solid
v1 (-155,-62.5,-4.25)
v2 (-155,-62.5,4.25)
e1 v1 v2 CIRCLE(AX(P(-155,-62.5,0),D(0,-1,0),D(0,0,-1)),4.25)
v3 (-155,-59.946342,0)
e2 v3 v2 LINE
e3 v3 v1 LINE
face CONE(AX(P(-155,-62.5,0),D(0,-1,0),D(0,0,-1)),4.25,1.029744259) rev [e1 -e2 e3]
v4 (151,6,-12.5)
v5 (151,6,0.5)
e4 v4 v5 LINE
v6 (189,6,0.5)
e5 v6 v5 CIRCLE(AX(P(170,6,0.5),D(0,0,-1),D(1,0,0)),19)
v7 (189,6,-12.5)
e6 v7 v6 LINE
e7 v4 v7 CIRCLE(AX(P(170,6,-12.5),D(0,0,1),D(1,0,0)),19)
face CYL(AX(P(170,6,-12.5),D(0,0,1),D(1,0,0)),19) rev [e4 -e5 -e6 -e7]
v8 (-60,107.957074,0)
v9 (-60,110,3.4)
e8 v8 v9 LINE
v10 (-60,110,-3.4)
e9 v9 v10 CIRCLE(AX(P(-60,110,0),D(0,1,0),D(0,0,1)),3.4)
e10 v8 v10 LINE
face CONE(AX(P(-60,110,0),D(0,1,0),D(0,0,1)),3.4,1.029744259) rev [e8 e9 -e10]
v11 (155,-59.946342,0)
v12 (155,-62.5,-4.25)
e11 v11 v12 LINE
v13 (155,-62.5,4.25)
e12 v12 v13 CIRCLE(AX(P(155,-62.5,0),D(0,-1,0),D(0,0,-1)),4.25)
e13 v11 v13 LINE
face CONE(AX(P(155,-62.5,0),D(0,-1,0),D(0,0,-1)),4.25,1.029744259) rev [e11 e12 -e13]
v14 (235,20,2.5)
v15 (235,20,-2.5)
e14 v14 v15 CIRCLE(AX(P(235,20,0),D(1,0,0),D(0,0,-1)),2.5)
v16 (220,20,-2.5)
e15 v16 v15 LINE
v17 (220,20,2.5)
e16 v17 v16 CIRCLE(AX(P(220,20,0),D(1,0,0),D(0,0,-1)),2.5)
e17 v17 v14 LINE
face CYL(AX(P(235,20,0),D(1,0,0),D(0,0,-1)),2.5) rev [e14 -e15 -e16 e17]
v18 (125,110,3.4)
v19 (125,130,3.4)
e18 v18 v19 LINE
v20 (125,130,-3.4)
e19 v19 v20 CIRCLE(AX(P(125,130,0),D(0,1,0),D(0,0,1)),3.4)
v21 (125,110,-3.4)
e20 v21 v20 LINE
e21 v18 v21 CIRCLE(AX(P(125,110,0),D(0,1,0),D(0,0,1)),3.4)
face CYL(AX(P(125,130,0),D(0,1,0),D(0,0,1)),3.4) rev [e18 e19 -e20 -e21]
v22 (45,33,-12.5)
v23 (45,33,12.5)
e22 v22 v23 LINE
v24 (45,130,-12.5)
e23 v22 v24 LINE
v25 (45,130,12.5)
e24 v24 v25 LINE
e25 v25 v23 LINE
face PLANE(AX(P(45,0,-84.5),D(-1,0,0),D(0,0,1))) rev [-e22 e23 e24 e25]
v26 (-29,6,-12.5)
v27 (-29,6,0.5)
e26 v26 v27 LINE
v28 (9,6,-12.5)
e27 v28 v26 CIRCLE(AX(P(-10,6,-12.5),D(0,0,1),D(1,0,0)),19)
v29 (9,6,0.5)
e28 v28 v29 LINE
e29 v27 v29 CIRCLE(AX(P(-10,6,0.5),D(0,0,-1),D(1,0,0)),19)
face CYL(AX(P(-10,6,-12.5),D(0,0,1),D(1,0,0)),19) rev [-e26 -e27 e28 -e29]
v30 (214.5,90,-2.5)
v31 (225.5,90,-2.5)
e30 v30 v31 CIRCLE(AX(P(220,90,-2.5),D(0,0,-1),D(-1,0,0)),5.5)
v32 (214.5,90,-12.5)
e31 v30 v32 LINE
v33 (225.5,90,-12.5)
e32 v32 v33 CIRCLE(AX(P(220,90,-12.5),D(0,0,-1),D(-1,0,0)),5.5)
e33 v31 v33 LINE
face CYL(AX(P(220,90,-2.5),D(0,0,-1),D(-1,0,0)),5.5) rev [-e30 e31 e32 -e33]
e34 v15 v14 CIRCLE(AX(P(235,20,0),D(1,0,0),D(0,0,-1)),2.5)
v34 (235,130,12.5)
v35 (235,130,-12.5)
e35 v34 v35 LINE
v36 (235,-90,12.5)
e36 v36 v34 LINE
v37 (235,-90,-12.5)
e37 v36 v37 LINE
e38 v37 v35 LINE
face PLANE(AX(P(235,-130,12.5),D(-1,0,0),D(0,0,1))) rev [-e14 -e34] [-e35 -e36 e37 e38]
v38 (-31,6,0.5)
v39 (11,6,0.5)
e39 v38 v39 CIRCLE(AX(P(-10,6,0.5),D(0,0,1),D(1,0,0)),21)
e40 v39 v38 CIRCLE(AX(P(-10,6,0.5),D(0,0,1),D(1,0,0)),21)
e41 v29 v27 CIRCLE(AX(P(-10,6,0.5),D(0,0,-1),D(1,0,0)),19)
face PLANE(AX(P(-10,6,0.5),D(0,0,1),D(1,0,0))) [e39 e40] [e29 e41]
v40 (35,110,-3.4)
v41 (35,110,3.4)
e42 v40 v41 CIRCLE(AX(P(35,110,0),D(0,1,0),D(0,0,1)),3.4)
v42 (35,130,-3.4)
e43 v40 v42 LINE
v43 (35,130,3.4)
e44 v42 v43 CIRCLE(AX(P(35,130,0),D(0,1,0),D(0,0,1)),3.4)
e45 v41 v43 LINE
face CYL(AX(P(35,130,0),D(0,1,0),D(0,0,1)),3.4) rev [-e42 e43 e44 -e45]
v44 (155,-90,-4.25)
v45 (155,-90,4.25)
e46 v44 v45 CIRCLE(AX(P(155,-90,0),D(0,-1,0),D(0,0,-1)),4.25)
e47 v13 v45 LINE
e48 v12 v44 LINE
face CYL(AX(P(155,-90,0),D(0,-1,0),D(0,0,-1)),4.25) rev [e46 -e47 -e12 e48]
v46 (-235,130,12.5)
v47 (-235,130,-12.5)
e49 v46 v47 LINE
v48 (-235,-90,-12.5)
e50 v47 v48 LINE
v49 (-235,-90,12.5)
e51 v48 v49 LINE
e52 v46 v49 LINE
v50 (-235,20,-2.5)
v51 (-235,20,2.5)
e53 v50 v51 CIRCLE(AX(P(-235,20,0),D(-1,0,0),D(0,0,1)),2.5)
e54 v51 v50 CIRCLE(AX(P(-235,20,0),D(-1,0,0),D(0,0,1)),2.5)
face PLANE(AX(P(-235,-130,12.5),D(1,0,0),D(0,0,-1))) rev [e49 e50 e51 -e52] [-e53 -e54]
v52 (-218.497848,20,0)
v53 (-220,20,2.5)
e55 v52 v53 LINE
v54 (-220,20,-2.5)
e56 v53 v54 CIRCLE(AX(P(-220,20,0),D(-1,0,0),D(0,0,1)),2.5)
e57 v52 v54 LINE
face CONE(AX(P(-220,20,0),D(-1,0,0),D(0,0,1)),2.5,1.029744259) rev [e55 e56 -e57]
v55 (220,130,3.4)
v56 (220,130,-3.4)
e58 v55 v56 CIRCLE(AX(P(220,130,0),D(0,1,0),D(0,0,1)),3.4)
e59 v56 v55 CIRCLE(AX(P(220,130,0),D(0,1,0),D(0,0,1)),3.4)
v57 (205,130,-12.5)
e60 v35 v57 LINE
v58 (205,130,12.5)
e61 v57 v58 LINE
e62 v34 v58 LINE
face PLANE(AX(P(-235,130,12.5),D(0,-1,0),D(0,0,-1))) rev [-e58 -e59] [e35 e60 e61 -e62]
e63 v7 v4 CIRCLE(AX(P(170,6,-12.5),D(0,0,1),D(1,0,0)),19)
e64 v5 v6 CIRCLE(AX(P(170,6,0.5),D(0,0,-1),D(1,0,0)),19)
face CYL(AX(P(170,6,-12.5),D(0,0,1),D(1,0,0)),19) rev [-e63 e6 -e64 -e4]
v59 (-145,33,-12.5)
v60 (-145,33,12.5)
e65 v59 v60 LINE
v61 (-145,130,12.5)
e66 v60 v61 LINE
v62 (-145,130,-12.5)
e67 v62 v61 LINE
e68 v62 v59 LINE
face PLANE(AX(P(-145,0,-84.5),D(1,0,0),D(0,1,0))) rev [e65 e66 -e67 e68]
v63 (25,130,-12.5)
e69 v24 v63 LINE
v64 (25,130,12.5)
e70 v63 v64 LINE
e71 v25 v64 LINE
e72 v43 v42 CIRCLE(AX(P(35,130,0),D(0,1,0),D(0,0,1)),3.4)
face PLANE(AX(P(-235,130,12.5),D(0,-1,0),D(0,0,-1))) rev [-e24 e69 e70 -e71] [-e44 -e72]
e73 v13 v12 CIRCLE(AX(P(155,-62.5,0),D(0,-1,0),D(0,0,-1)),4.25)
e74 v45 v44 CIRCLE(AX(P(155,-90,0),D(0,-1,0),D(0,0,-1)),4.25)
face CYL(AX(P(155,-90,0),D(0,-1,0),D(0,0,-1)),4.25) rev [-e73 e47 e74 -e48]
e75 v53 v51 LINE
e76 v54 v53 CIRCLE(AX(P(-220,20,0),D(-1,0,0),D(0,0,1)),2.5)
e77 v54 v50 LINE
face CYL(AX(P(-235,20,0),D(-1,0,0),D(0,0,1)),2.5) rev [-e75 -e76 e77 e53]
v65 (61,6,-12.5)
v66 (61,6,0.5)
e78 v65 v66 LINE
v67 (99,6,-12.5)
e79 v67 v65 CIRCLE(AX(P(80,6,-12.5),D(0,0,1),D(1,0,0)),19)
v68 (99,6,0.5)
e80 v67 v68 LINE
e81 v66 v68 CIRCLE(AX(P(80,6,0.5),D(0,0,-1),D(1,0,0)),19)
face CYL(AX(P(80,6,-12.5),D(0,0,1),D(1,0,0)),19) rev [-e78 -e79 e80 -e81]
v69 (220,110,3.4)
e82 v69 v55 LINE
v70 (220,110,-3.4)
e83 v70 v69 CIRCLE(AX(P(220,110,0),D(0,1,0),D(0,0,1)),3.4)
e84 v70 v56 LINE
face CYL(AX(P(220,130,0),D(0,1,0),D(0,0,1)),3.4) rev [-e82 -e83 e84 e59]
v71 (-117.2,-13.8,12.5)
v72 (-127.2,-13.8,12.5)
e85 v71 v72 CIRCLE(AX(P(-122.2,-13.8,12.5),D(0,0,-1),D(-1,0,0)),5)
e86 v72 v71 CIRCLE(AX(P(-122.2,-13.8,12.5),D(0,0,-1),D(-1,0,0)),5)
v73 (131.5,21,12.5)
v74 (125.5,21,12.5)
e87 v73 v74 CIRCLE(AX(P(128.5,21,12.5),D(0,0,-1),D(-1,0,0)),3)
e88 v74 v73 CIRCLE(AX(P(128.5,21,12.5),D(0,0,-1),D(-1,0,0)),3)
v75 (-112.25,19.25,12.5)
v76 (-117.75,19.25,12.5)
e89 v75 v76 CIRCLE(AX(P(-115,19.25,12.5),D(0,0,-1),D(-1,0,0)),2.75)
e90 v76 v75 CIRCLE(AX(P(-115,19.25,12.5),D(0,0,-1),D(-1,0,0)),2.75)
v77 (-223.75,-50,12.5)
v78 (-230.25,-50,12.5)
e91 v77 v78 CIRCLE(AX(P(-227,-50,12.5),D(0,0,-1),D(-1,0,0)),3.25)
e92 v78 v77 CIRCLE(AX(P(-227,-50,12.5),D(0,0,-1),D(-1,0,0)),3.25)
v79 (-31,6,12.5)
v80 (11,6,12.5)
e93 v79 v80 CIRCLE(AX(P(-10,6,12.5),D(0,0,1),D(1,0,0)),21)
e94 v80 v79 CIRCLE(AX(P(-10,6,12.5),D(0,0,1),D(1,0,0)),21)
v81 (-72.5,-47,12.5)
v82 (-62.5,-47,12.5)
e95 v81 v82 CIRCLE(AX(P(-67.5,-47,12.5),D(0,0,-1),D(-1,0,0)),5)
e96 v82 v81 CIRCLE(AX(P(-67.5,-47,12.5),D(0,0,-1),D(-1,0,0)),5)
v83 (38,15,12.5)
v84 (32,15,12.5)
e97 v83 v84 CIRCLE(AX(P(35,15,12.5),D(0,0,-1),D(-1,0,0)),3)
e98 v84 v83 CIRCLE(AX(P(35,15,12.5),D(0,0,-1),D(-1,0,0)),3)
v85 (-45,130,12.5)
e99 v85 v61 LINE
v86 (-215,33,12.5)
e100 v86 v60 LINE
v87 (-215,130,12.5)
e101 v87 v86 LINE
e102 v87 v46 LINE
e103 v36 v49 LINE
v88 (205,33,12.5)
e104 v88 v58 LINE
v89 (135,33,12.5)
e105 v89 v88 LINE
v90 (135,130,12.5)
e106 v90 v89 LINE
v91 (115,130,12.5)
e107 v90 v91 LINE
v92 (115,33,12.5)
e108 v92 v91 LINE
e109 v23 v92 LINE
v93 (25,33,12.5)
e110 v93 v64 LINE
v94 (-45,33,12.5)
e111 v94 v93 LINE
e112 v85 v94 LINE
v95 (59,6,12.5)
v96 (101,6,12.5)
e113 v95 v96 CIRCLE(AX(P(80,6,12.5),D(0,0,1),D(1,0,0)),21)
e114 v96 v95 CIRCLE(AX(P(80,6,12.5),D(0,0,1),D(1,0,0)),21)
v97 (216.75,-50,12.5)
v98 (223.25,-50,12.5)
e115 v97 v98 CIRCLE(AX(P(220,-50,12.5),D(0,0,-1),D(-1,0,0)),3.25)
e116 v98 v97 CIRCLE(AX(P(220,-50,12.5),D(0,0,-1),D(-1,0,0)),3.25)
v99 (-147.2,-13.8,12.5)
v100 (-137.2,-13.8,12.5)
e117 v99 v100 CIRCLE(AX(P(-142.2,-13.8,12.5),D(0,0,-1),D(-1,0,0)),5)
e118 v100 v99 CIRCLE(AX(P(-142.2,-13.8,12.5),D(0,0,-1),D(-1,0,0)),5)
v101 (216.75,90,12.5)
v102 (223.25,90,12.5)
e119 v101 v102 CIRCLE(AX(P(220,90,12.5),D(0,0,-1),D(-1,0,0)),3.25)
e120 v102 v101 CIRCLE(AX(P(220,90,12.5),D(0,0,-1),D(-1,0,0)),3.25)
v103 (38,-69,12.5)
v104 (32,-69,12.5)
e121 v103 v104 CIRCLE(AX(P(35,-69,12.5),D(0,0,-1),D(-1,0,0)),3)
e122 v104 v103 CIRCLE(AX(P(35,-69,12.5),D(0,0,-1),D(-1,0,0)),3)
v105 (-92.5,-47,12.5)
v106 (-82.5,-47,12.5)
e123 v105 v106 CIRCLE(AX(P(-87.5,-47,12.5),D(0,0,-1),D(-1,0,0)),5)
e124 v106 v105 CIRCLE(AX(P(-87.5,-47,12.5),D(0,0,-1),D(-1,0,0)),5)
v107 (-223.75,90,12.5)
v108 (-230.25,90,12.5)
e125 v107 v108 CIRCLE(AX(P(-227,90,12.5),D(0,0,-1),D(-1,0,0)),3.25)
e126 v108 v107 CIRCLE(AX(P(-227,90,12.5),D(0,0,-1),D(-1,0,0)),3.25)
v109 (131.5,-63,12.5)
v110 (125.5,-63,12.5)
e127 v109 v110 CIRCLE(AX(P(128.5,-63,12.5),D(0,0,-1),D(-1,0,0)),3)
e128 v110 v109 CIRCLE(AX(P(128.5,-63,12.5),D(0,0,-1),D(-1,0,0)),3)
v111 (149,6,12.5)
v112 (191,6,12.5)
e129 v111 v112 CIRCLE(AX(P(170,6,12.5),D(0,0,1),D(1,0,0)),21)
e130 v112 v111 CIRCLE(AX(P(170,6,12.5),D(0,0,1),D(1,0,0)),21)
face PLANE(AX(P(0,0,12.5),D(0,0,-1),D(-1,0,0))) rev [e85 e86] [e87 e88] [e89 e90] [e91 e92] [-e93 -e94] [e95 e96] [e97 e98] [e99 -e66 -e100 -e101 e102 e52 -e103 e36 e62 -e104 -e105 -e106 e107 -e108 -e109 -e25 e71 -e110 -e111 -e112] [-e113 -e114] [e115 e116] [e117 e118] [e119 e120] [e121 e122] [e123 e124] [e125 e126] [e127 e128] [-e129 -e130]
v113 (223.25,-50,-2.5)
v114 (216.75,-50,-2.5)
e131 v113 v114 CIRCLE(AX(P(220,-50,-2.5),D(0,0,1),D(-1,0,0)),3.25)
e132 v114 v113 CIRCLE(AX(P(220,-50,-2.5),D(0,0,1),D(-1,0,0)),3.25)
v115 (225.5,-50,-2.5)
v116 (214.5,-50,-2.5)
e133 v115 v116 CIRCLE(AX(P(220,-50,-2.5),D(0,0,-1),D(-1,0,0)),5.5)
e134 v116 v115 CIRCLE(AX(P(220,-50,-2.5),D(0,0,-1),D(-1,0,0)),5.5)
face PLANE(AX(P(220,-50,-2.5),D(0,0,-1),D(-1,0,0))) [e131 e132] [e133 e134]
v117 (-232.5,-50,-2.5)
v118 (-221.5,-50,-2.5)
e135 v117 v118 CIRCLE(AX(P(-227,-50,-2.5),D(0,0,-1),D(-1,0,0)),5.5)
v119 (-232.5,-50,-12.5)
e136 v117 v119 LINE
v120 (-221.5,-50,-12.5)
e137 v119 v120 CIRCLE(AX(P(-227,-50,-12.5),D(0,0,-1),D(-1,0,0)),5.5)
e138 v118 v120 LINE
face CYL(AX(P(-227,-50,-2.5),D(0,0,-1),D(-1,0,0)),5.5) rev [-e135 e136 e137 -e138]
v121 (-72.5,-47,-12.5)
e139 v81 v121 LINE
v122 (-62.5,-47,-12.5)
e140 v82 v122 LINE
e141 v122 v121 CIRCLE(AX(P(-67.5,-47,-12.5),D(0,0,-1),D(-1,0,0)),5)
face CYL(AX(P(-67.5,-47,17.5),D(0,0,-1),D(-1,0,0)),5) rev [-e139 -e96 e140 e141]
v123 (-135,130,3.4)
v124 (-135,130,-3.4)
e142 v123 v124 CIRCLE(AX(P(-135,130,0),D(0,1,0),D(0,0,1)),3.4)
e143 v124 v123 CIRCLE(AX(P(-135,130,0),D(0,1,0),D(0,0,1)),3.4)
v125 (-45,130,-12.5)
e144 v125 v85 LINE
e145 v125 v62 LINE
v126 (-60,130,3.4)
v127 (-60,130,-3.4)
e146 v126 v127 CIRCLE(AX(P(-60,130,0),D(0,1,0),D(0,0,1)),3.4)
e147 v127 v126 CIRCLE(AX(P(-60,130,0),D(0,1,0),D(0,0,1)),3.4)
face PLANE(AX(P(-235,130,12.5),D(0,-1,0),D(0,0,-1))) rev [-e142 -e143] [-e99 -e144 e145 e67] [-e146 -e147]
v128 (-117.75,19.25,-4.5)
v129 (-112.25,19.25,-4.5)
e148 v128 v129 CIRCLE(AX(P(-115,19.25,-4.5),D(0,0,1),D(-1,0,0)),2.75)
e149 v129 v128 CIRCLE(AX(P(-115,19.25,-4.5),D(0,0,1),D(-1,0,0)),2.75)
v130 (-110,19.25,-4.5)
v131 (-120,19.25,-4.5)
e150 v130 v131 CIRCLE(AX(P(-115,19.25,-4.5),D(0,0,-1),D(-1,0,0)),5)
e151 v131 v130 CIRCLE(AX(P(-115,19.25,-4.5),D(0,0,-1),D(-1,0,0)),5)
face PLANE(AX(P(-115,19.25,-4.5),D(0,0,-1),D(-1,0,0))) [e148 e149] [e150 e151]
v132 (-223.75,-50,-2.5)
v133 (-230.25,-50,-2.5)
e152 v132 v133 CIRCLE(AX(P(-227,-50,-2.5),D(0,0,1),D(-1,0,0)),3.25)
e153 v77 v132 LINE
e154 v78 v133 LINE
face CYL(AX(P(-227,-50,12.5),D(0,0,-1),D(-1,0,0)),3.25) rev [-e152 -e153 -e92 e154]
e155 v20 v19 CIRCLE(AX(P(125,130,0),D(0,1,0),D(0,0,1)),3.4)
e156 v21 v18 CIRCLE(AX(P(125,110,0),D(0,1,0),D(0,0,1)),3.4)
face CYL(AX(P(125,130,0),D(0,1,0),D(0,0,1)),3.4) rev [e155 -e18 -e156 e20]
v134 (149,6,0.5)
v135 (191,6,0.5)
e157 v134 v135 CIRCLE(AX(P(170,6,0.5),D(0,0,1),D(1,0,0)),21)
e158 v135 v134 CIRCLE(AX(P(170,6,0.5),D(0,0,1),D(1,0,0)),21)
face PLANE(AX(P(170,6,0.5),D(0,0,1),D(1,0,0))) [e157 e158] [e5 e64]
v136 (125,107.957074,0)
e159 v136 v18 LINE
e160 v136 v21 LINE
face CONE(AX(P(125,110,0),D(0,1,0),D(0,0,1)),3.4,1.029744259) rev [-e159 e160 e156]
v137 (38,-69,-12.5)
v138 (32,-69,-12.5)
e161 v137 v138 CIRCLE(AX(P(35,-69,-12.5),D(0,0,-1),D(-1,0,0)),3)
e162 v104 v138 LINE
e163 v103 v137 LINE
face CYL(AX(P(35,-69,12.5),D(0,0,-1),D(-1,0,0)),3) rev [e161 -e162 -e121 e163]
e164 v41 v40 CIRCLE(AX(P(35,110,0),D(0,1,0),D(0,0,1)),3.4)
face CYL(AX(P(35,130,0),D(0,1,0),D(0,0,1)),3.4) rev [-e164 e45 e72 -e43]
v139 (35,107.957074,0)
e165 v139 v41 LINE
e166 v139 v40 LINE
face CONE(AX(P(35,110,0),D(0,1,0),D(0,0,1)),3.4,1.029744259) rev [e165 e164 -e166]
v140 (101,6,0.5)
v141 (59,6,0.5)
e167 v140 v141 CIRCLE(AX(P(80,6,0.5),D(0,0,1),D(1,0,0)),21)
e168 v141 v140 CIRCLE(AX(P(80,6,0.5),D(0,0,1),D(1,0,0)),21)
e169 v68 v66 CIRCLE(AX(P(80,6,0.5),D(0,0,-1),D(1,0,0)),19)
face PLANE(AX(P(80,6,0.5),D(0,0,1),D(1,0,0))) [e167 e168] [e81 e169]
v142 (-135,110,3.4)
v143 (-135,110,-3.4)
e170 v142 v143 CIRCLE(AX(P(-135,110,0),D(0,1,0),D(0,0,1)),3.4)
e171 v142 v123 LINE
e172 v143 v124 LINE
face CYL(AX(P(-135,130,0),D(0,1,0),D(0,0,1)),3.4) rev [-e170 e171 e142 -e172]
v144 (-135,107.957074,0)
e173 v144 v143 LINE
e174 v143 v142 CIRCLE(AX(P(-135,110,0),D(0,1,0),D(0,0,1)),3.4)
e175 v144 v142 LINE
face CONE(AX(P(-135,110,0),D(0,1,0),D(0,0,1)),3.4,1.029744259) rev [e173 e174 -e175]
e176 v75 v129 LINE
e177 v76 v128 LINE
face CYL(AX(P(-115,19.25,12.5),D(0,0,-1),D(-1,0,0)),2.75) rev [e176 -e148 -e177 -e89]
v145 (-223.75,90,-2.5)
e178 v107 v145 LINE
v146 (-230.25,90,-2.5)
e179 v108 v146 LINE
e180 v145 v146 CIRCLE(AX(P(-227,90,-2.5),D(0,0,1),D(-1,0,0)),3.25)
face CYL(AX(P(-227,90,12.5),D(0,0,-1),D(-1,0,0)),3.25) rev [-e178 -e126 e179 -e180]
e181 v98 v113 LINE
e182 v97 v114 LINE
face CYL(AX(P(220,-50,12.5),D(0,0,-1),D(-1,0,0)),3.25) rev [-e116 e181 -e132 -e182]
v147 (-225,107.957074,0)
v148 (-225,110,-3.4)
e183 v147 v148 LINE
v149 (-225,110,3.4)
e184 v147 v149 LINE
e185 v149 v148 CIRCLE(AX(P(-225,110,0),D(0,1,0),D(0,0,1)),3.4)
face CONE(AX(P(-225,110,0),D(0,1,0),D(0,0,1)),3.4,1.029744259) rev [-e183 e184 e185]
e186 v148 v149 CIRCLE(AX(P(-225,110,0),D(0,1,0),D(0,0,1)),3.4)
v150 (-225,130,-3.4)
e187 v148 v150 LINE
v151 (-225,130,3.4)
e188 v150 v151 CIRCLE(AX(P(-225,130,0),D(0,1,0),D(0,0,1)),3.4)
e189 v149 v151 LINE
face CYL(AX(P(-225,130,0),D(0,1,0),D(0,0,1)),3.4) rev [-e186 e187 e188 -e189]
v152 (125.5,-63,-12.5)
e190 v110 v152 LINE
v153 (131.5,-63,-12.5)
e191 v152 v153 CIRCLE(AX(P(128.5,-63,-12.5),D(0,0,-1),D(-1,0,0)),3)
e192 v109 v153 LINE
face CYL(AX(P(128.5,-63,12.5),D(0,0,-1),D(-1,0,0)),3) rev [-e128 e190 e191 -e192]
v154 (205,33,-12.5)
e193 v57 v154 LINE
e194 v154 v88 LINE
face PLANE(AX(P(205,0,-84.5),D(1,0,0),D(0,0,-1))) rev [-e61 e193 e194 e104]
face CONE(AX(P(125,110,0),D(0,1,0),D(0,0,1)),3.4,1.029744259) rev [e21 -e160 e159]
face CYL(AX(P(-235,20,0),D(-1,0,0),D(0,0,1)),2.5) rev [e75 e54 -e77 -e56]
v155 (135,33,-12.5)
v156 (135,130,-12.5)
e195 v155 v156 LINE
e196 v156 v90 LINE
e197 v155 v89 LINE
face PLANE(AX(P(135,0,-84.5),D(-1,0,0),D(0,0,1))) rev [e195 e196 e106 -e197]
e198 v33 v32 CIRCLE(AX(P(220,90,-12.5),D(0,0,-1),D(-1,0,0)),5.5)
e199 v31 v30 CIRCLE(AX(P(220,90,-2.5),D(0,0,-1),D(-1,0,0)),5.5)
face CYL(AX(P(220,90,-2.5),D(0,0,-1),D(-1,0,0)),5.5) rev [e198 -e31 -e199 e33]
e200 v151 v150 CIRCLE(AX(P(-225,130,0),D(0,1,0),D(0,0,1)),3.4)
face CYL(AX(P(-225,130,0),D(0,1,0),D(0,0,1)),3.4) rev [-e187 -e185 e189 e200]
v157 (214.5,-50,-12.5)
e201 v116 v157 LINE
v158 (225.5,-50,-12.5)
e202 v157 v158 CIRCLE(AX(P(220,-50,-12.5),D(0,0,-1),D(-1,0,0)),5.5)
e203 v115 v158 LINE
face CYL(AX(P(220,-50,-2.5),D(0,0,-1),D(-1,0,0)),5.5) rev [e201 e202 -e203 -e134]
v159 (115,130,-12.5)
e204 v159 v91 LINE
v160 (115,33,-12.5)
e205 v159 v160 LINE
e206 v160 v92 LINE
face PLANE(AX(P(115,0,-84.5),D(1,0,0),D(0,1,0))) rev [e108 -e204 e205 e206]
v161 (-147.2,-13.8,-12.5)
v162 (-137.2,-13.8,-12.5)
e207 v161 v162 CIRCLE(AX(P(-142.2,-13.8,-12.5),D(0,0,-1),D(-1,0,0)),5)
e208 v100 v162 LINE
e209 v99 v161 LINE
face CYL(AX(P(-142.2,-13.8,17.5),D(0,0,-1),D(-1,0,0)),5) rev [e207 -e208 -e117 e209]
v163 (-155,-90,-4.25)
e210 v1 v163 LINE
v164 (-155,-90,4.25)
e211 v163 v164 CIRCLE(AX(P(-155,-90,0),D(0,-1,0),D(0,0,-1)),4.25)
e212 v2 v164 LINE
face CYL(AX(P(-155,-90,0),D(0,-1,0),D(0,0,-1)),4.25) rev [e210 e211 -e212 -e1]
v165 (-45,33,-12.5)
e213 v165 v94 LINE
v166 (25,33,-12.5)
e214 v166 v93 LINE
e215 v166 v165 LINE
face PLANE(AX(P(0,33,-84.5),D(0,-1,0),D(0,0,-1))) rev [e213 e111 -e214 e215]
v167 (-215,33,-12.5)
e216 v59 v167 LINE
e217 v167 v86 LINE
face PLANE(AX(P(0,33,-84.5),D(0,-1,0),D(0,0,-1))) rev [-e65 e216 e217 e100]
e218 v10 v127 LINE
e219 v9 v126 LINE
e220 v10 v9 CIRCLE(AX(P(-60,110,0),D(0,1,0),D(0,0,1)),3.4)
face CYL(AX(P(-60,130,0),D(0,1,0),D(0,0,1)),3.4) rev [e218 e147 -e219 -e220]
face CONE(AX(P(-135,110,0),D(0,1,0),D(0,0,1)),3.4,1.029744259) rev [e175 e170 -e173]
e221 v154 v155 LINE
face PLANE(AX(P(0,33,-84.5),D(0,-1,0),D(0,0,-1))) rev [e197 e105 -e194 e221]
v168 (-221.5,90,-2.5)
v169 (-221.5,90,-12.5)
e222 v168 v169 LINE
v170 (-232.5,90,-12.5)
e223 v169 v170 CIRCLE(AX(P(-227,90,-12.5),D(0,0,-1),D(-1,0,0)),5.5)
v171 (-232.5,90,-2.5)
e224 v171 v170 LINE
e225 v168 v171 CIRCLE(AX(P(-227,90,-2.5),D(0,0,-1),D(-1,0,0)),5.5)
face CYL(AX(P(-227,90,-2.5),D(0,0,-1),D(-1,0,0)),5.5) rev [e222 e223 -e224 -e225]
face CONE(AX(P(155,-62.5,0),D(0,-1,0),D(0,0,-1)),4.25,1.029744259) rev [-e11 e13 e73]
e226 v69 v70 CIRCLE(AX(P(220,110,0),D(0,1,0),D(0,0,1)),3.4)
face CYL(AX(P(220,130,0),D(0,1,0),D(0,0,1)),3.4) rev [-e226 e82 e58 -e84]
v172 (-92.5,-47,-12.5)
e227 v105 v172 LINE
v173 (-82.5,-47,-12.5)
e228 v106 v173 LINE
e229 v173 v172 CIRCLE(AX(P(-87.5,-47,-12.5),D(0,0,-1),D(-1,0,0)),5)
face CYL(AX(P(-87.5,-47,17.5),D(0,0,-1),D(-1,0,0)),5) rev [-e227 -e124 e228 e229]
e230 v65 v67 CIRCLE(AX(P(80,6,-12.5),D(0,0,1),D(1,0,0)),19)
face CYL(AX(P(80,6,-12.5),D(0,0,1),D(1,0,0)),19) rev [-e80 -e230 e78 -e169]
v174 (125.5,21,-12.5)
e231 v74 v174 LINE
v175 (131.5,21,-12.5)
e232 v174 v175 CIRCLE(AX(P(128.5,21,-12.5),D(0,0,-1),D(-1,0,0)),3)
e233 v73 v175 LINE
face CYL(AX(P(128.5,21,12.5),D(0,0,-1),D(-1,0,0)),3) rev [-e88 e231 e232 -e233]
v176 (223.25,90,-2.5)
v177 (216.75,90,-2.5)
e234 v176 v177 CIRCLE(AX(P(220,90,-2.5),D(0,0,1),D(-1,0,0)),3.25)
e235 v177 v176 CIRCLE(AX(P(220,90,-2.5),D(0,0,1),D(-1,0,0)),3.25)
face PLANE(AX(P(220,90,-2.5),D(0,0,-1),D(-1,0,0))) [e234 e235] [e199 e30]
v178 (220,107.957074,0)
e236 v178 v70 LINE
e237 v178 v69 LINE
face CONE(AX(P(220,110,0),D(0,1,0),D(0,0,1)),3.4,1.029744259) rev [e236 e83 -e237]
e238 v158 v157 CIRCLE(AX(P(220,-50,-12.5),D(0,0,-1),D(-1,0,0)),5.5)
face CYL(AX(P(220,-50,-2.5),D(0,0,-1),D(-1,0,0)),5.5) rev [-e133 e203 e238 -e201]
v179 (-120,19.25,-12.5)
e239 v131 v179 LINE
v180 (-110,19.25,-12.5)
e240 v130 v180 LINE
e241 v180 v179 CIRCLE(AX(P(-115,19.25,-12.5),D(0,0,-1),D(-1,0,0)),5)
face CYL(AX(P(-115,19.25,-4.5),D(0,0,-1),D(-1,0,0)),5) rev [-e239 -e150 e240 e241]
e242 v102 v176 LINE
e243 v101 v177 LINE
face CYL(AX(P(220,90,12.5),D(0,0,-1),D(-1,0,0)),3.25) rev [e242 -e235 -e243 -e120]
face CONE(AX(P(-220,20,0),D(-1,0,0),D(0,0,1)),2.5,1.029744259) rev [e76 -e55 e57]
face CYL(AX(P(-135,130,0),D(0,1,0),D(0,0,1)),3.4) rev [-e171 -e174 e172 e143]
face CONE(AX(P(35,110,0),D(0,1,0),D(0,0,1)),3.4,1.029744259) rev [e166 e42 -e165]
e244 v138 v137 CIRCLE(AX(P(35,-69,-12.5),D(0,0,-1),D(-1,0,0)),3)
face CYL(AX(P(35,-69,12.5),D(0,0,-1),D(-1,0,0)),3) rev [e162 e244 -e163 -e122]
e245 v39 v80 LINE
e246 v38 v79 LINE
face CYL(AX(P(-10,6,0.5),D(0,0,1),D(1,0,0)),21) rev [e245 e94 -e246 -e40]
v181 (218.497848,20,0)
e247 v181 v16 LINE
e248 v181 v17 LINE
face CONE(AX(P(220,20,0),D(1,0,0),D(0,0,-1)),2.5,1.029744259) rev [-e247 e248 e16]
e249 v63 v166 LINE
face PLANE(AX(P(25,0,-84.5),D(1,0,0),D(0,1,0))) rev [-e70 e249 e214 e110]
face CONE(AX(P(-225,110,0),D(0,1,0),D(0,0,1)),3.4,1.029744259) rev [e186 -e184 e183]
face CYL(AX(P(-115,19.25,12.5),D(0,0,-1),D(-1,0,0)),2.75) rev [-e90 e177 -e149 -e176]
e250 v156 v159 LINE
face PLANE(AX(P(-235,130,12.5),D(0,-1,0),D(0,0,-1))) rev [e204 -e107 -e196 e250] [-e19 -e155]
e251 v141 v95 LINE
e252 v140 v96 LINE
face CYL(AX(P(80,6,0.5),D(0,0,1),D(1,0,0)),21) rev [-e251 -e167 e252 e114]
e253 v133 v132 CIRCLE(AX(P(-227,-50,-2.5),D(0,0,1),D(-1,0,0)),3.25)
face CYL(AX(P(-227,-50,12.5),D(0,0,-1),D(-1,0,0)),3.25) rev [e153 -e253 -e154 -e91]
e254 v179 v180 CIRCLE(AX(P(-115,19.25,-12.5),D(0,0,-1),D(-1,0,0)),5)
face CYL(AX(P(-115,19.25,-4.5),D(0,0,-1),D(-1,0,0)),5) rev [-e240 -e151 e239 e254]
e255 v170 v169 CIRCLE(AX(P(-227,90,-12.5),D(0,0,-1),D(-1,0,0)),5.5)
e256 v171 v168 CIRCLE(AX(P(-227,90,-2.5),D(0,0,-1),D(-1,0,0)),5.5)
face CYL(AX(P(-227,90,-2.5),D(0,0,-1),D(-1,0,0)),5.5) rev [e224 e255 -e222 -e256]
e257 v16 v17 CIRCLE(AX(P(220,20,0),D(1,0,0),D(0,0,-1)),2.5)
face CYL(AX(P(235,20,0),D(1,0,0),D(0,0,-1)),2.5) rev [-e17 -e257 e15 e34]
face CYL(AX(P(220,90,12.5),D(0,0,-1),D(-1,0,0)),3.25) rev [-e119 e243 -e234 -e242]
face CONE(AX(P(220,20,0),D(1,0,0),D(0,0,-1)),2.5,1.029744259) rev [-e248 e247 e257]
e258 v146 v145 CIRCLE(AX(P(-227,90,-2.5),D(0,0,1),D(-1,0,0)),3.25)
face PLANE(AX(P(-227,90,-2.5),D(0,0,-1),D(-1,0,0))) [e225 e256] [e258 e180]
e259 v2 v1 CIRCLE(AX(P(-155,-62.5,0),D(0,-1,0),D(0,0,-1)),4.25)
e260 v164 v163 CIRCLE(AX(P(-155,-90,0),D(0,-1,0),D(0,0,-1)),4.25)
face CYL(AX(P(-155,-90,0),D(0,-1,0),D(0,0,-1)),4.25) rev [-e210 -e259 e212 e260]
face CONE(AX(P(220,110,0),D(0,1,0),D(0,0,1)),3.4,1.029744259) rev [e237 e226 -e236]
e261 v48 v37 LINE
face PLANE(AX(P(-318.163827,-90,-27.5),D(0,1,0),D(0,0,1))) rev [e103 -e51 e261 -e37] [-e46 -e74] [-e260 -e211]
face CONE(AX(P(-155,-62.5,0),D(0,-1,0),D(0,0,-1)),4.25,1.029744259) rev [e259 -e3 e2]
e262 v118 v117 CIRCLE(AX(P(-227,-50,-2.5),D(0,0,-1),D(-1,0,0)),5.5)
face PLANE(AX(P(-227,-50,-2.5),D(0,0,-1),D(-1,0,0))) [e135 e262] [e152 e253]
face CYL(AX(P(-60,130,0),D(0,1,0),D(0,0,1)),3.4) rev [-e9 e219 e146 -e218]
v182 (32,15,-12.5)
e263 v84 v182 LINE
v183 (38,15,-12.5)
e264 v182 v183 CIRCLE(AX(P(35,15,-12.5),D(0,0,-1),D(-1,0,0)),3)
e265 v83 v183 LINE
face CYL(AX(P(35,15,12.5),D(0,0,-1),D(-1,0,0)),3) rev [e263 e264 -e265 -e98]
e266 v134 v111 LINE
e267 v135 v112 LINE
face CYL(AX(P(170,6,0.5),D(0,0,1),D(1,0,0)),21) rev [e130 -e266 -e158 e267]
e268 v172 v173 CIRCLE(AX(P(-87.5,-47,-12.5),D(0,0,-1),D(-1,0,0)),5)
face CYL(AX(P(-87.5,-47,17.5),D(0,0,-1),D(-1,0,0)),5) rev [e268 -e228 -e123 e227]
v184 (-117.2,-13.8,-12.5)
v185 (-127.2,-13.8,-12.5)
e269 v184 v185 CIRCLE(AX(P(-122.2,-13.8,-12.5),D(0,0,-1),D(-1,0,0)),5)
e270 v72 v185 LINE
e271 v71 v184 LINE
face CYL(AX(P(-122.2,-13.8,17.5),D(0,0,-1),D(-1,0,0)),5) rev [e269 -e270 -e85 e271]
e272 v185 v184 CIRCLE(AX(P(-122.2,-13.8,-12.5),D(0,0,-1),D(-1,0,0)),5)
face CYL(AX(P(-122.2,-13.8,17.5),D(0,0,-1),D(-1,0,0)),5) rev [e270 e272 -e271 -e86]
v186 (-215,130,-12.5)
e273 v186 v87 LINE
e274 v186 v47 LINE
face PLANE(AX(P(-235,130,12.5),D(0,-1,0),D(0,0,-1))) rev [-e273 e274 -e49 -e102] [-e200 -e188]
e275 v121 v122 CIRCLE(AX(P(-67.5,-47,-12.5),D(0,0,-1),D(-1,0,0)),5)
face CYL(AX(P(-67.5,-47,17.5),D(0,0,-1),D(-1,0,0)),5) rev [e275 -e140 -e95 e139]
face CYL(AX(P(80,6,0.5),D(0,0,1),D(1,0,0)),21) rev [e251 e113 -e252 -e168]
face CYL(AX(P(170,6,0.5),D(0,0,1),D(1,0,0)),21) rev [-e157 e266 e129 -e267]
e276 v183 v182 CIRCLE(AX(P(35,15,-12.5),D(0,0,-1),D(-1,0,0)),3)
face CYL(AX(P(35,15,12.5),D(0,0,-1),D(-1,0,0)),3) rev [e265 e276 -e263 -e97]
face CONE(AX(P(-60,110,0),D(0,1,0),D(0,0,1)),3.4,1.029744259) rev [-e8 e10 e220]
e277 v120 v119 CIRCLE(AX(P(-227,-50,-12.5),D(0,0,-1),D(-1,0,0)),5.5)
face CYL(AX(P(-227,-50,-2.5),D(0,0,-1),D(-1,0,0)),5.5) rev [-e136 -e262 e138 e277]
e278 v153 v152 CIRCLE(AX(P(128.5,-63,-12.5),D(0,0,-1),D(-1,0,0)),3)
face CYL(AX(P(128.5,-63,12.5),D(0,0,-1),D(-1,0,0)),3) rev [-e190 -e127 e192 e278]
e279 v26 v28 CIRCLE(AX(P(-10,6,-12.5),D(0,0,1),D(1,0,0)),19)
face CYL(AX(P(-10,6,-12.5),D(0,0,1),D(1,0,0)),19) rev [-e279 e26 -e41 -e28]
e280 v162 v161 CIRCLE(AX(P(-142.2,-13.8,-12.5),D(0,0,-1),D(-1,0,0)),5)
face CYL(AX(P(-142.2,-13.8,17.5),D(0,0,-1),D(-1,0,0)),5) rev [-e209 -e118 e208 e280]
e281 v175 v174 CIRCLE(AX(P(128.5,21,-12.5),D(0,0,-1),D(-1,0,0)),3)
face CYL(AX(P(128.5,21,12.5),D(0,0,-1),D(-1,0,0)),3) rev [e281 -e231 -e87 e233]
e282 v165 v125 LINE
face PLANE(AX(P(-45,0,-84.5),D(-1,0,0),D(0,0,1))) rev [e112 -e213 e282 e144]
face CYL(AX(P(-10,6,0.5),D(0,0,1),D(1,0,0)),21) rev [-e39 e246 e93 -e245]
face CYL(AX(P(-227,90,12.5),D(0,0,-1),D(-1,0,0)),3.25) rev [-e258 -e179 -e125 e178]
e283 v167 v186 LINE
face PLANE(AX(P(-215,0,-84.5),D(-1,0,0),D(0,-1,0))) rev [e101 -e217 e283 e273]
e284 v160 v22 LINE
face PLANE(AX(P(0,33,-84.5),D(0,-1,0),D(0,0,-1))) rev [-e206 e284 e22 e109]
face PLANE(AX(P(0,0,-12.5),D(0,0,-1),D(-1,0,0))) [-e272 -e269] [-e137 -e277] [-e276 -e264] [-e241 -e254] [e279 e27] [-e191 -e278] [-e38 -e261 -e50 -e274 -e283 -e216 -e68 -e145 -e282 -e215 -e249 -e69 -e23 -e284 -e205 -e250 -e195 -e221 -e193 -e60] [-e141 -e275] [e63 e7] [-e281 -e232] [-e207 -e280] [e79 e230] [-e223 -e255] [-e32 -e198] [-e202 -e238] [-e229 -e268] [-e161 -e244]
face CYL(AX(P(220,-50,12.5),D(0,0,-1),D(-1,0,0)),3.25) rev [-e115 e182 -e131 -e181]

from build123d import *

# Parameters (mm, degrees)
SKETCH1_W                       = 470
SKETCH1_H                       = 260
BOSS_EXTRUDE1_DEPTH             = 12.5
SKETCH4_W                       = 70
SKETCH4_H                       = 97
CUT_EXTRUDE3_DEPTH              = 97
SKETCH8_W                       = 627.570760349
SKETCH8_H                       = 104.374926458
CUT_EXTRUDE7_DEPTH              = 40
M8_TAPPED_HOLE1_D               = 6.8
M8_TAPPED_HOLE1_DEPTH           = 20
M8_TAPPED_HOLE1_TIP             = 2.042926105
M10_TAPPED_HOLE1_D              = 8.5
M10_TAPPED_HOLE1_DEPTH          = 27.5
M10_TAPPED_HOLE1_TIP            = 2.553657631
SKETCH17_R                      = 19
CUT_EXTRUDE10_DEPTH             = 270.722079185
SKETCH18_R                      = 21
CUT_EXTRUDE11_DEPTH             = 12
SKETCH22_R                      = 3
CUT_EXTRUDE13_DEPTH             = 270.722079185
SKETCH23_R                      = 3.25
CUT_EXTRUDE14_DEPTH             = 270.722079185
SKETCH24_R                      = 5.5
CUT_EXTRUDE15_DEPTH             = 10
LPATTERN1_COUNT                 = 2
LPATTERN1_PITCH                 = 447
SKETCH26_R                      = 2.75
CUT_EXTRUDE17_DEPTH             = 270.722079185
SKETCH27_R                      = 5
CUT_EXTRUDE18_DEPTH             = 8
SKETCH28_R                      = 5
CUT_EXTRUDE19_DEPTH             = 30
M6_TAPPED_HOLE1_D               = 5
M6_TAPPED_HOLE1_DEPTH           = 15
M6_TAPPED_HOLE1_TIP             = 1.502151548
M6_TAPPED_HOLE1_ON_FACE_2_D     = 5
M6_TAPPED_HOLE1_ON_FACE_2_DEPTH = 15
M6_TAPPED_HOLE1_ON_FACE_2_TIP   = 1.502151548


with BuildPart() as part:
    # Sketch1 → Boss-Extrude1 (new, symmetric)
    with BuildSketch(Plane.XY):
        Rectangle(SKETCH1_W, SKETCH1_H)
    extrude(amount=BOSS_EXTRUDE1_DEPTH, both=True)

    # Sketch4 → Cut-Extrude3 (cut)
    with BuildSketch(Plane.XY.offset(12.5)):
        with Locations((-180, 81.5)):
            Rectangle(SKETCH4_W, SKETCH4_H)
        with Locations((-10, 81.5)):
            Rectangle(SKETCH4_W, SKETCH4_H)
        with Locations((80, 81.5)):
            Rectangle(SKETCH4_W, SKETCH4_H)
        with Locations((170, 81.5)):
            Rectangle(SKETCH4_W, SKETCH4_H)
    extrude(amount=-CUT_EXTRUDE3_DEPTH, mode=Mode.SUBTRACT)

    # Sketch8 → Cut-Extrude7 (cut)
    with BuildSketch(Plane.XY.offset(12.5)):
        with Locations((-4.378447024, -142.187463229)):
            Rectangle(SKETCH8_W, SKETCH8_H)
    extrude(amount=-CUT_EXTRUDE7_DEPTH, mode=Mode.SUBTRACT)

    # M8 Tapped Hole1
    with Locations(Plane(origin=(0, 130, 0), x_dir=(1, 0, 0), z_dir=(0, 1, 0))):
        with Locations((-225, 0), (-135, 0), (35, 0), (125, 0), (220, 0), (-60, 0)):
            Hole(M8_TAPPED_HOLE1_D / 2, depth=M8_TAPPED_HOLE1_DEPTH)
            with Locations((0, 0, -(M8_TAPPED_HOLE1_DEPTH + M8_TAPPED_HOLE1_TIP / 2))):  # 118° drill point
                Cone(0, M8_TAPPED_HOLE1_D / 2, M8_TAPPED_HOLE1_TIP, mode=Mode.SUBTRACT)

    # M10 Tapped Hole1
    with Locations(Plane(origin=(0, -90, 0), x_dir=(-1, 0, 0), z_dir=(0, -1, 0))):
        with Locations((-155, 0), (155, 0)):
            Hole(M10_TAPPED_HOLE1_D / 2, depth=M10_TAPPED_HOLE1_DEPTH)
            with Locations((0, 0, -(M10_TAPPED_HOLE1_DEPTH + M10_TAPPED_HOLE1_TIP / 2))):  # 118° drill point
                Cone(0, M10_TAPPED_HOLE1_D / 2, M10_TAPPED_HOLE1_TIP, mode=Mode.SUBTRACT)

    # Sketch17 → Cut-Extrude10 (cut, through all)
    with BuildSketch(Plane.XY.offset(12.5)):
        with Locations((170, 6)):
            Circle(SKETCH17_R)
        with Locations((80, 6)):
            Circle(SKETCH17_R)
        with Locations((-10, 6)):
            Circle(SKETCH17_R)
    extrude(amount=-CUT_EXTRUDE10_DEPTH, mode=Mode.SUBTRACT)

    # Sketch18 → Cut-Extrude11 (cut)
    with BuildSketch(Plane.XY.offset(12.5)):
        with Locations((170, 6)):
            Circle(SKETCH18_R)
        with Locations((80, 6)):
            Circle(SKETCH18_R)
        with Locations((-10, 6)):
            Circle(SKETCH18_R)
    extrude(amount=-CUT_EXTRUDE11_DEPTH, mode=Mode.SUBTRACT)

    # Sketch22 → Cut-Extrude13 (cut, through all)
    with BuildSketch(Plane(origin=(0, 0, -12.5), x_dir=(-1, 0, 0), z_dir=(0, 0, -1))):
        with Locations((-128.5, 21)):
            Circle(SKETCH22_R)
        with Locations((-128.5, -63)):
            Circle(SKETCH22_R)
        with Locations((-35, 15)):
            Circle(SKETCH22_R)
        with Locations((-35, -69)):
            Circle(SKETCH22_R)
    extrude(amount=-CUT_EXTRUDE13_DEPTH, mode=Mode.SUBTRACT)

    # Sketch23 → Cut-Extrude14 (cut, through all)
    with BuildSketch(Plane(origin=(0, 0, -12.5), x_dir=(-1, 0, 0), z_dir=(0, 0, -1))):
        with Locations((-220, 90)):
            Circle(SKETCH23_R)
        with Locations((-220, -50)):
            Circle(SKETCH23_R)
    cut_extrude14 = extrude(amount=-CUT_EXTRUDE14_DEPTH, mode=Mode.SUBTRACT)

    # Sketch24 → Cut-Extrude15 (cut)
    with BuildSketch(Plane(origin=(0, 0, -12.5), x_dir=(-1, 0, 0), z_dir=(0, 0, -1))):
        with Locations((-220, 90)):
            Circle(SKETCH24_R)
        with Locations((-220, -50)):
            Circle(SKETCH24_R)
    cut_extrude15 = extrude(amount=-CUT_EXTRUDE15_DEPTH, mode=Mode.SUBTRACT)

    # LPattern1: Cut-Extrude14, Cut-Extrude15 ×2
    with Locations(*[(-i * LPATTERN1_PITCH, 0, 0) for i in range(1, LPATTERN1_COUNT)]):
        add(cut_extrude14, mode=Mode.SUBTRACT)
        add(cut_extrude15, mode=Mode.SUBTRACT)

    # Sketch26 → Cut-Extrude17 (cut, through all)
    with BuildSketch(Plane(origin=(0, 0, -12.5), x_dir=(-1, 0, 0), z_dir=(0, 0, -1))):
        with Locations((115, 19.25)):
            Circle(SKETCH26_R)
    extrude(amount=-CUT_EXTRUDE17_DEPTH, mode=Mode.SUBTRACT)

    # Sketch27 → Cut-Extrude18 (cut)
    with BuildSketch(Plane(origin=(0, 0, -12.5), x_dir=(-1, 0, 0), z_dir=(0, 0, -1))):
        with Locations((115, 19.25)):
            Circle(SKETCH27_R)
    extrude(amount=-CUT_EXTRUDE18_DEPTH, mode=Mode.SUBTRACT)

    # Sketch28 → Cut-Extrude19 (cut)
    with BuildSketch(Plane(origin=(0, 0, -12.5), x_dir=(-1, 0, 0), z_dir=(0, 0, -1))):
        with Locations((67.5, -47)):
            Circle(SKETCH28_R)
        with Locations((87.5, -47)):
            Circle(SKETCH28_R)
        with Locations((122.2, -13.8)):
            Circle(SKETCH28_R)
        with Locations((142.2, -13.8)):
            Circle(SKETCH28_R)
    extrude(amount=-CUT_EXTRUDE19_DEPTH, mode=Mode.SUBTRACT)

    # M6 Tapped Hole1
    with Locations(Plane(origin=(-235, 20, 0), x_dir=(0, 0, -1), z_dir=(-1, 0, 0))):
        with Locations((0, 0)):
            Hole(M6_TAPPED_HOLE1_D / 2, depth=M6_TAPPED_HOLE1_DEPTH)
            with Locations((0, 0, -(M6_TAPPED_HOLE1_DEPTH + M6_TAPPED_HOLE1_TIP / 2))):  # 118° drill point
                Cone(0, M6_TAPPED_HOLE1_D / 2, M6_TAPPED_HOLE1_TIP, mode=Mode.SUBTRACT)

    # M6 Tapped Hole1 on face 2
    with Locations(Plane(origin=(235, 20, 0), x_dir=(0, 0, 1), z_dir=(1, 0, 0))):
        with Locations((0, 0)):
            Hole(M6_TAPPED_HOLE1_ON_FACE_2_D / 2, depth=M6_TAPPED_HOLE1_ON_FACE_2_DEPTH)
            with Locations((0, 0, -(M6_TAPPED_HOLE1_ON_FACE_2_DEPTH + M6_TAPPED_HOLE1_ON_FACE_2_TIP / 2))):  # 118° drill point
                Cone(0, M6_TAPPED_HOLE1_ON_FACE_2_D / 2, M6_TAPPED_HOLE1_ON_FACE_2_TIP, mode=Mode.SUBTRACT)


solid = part.part
